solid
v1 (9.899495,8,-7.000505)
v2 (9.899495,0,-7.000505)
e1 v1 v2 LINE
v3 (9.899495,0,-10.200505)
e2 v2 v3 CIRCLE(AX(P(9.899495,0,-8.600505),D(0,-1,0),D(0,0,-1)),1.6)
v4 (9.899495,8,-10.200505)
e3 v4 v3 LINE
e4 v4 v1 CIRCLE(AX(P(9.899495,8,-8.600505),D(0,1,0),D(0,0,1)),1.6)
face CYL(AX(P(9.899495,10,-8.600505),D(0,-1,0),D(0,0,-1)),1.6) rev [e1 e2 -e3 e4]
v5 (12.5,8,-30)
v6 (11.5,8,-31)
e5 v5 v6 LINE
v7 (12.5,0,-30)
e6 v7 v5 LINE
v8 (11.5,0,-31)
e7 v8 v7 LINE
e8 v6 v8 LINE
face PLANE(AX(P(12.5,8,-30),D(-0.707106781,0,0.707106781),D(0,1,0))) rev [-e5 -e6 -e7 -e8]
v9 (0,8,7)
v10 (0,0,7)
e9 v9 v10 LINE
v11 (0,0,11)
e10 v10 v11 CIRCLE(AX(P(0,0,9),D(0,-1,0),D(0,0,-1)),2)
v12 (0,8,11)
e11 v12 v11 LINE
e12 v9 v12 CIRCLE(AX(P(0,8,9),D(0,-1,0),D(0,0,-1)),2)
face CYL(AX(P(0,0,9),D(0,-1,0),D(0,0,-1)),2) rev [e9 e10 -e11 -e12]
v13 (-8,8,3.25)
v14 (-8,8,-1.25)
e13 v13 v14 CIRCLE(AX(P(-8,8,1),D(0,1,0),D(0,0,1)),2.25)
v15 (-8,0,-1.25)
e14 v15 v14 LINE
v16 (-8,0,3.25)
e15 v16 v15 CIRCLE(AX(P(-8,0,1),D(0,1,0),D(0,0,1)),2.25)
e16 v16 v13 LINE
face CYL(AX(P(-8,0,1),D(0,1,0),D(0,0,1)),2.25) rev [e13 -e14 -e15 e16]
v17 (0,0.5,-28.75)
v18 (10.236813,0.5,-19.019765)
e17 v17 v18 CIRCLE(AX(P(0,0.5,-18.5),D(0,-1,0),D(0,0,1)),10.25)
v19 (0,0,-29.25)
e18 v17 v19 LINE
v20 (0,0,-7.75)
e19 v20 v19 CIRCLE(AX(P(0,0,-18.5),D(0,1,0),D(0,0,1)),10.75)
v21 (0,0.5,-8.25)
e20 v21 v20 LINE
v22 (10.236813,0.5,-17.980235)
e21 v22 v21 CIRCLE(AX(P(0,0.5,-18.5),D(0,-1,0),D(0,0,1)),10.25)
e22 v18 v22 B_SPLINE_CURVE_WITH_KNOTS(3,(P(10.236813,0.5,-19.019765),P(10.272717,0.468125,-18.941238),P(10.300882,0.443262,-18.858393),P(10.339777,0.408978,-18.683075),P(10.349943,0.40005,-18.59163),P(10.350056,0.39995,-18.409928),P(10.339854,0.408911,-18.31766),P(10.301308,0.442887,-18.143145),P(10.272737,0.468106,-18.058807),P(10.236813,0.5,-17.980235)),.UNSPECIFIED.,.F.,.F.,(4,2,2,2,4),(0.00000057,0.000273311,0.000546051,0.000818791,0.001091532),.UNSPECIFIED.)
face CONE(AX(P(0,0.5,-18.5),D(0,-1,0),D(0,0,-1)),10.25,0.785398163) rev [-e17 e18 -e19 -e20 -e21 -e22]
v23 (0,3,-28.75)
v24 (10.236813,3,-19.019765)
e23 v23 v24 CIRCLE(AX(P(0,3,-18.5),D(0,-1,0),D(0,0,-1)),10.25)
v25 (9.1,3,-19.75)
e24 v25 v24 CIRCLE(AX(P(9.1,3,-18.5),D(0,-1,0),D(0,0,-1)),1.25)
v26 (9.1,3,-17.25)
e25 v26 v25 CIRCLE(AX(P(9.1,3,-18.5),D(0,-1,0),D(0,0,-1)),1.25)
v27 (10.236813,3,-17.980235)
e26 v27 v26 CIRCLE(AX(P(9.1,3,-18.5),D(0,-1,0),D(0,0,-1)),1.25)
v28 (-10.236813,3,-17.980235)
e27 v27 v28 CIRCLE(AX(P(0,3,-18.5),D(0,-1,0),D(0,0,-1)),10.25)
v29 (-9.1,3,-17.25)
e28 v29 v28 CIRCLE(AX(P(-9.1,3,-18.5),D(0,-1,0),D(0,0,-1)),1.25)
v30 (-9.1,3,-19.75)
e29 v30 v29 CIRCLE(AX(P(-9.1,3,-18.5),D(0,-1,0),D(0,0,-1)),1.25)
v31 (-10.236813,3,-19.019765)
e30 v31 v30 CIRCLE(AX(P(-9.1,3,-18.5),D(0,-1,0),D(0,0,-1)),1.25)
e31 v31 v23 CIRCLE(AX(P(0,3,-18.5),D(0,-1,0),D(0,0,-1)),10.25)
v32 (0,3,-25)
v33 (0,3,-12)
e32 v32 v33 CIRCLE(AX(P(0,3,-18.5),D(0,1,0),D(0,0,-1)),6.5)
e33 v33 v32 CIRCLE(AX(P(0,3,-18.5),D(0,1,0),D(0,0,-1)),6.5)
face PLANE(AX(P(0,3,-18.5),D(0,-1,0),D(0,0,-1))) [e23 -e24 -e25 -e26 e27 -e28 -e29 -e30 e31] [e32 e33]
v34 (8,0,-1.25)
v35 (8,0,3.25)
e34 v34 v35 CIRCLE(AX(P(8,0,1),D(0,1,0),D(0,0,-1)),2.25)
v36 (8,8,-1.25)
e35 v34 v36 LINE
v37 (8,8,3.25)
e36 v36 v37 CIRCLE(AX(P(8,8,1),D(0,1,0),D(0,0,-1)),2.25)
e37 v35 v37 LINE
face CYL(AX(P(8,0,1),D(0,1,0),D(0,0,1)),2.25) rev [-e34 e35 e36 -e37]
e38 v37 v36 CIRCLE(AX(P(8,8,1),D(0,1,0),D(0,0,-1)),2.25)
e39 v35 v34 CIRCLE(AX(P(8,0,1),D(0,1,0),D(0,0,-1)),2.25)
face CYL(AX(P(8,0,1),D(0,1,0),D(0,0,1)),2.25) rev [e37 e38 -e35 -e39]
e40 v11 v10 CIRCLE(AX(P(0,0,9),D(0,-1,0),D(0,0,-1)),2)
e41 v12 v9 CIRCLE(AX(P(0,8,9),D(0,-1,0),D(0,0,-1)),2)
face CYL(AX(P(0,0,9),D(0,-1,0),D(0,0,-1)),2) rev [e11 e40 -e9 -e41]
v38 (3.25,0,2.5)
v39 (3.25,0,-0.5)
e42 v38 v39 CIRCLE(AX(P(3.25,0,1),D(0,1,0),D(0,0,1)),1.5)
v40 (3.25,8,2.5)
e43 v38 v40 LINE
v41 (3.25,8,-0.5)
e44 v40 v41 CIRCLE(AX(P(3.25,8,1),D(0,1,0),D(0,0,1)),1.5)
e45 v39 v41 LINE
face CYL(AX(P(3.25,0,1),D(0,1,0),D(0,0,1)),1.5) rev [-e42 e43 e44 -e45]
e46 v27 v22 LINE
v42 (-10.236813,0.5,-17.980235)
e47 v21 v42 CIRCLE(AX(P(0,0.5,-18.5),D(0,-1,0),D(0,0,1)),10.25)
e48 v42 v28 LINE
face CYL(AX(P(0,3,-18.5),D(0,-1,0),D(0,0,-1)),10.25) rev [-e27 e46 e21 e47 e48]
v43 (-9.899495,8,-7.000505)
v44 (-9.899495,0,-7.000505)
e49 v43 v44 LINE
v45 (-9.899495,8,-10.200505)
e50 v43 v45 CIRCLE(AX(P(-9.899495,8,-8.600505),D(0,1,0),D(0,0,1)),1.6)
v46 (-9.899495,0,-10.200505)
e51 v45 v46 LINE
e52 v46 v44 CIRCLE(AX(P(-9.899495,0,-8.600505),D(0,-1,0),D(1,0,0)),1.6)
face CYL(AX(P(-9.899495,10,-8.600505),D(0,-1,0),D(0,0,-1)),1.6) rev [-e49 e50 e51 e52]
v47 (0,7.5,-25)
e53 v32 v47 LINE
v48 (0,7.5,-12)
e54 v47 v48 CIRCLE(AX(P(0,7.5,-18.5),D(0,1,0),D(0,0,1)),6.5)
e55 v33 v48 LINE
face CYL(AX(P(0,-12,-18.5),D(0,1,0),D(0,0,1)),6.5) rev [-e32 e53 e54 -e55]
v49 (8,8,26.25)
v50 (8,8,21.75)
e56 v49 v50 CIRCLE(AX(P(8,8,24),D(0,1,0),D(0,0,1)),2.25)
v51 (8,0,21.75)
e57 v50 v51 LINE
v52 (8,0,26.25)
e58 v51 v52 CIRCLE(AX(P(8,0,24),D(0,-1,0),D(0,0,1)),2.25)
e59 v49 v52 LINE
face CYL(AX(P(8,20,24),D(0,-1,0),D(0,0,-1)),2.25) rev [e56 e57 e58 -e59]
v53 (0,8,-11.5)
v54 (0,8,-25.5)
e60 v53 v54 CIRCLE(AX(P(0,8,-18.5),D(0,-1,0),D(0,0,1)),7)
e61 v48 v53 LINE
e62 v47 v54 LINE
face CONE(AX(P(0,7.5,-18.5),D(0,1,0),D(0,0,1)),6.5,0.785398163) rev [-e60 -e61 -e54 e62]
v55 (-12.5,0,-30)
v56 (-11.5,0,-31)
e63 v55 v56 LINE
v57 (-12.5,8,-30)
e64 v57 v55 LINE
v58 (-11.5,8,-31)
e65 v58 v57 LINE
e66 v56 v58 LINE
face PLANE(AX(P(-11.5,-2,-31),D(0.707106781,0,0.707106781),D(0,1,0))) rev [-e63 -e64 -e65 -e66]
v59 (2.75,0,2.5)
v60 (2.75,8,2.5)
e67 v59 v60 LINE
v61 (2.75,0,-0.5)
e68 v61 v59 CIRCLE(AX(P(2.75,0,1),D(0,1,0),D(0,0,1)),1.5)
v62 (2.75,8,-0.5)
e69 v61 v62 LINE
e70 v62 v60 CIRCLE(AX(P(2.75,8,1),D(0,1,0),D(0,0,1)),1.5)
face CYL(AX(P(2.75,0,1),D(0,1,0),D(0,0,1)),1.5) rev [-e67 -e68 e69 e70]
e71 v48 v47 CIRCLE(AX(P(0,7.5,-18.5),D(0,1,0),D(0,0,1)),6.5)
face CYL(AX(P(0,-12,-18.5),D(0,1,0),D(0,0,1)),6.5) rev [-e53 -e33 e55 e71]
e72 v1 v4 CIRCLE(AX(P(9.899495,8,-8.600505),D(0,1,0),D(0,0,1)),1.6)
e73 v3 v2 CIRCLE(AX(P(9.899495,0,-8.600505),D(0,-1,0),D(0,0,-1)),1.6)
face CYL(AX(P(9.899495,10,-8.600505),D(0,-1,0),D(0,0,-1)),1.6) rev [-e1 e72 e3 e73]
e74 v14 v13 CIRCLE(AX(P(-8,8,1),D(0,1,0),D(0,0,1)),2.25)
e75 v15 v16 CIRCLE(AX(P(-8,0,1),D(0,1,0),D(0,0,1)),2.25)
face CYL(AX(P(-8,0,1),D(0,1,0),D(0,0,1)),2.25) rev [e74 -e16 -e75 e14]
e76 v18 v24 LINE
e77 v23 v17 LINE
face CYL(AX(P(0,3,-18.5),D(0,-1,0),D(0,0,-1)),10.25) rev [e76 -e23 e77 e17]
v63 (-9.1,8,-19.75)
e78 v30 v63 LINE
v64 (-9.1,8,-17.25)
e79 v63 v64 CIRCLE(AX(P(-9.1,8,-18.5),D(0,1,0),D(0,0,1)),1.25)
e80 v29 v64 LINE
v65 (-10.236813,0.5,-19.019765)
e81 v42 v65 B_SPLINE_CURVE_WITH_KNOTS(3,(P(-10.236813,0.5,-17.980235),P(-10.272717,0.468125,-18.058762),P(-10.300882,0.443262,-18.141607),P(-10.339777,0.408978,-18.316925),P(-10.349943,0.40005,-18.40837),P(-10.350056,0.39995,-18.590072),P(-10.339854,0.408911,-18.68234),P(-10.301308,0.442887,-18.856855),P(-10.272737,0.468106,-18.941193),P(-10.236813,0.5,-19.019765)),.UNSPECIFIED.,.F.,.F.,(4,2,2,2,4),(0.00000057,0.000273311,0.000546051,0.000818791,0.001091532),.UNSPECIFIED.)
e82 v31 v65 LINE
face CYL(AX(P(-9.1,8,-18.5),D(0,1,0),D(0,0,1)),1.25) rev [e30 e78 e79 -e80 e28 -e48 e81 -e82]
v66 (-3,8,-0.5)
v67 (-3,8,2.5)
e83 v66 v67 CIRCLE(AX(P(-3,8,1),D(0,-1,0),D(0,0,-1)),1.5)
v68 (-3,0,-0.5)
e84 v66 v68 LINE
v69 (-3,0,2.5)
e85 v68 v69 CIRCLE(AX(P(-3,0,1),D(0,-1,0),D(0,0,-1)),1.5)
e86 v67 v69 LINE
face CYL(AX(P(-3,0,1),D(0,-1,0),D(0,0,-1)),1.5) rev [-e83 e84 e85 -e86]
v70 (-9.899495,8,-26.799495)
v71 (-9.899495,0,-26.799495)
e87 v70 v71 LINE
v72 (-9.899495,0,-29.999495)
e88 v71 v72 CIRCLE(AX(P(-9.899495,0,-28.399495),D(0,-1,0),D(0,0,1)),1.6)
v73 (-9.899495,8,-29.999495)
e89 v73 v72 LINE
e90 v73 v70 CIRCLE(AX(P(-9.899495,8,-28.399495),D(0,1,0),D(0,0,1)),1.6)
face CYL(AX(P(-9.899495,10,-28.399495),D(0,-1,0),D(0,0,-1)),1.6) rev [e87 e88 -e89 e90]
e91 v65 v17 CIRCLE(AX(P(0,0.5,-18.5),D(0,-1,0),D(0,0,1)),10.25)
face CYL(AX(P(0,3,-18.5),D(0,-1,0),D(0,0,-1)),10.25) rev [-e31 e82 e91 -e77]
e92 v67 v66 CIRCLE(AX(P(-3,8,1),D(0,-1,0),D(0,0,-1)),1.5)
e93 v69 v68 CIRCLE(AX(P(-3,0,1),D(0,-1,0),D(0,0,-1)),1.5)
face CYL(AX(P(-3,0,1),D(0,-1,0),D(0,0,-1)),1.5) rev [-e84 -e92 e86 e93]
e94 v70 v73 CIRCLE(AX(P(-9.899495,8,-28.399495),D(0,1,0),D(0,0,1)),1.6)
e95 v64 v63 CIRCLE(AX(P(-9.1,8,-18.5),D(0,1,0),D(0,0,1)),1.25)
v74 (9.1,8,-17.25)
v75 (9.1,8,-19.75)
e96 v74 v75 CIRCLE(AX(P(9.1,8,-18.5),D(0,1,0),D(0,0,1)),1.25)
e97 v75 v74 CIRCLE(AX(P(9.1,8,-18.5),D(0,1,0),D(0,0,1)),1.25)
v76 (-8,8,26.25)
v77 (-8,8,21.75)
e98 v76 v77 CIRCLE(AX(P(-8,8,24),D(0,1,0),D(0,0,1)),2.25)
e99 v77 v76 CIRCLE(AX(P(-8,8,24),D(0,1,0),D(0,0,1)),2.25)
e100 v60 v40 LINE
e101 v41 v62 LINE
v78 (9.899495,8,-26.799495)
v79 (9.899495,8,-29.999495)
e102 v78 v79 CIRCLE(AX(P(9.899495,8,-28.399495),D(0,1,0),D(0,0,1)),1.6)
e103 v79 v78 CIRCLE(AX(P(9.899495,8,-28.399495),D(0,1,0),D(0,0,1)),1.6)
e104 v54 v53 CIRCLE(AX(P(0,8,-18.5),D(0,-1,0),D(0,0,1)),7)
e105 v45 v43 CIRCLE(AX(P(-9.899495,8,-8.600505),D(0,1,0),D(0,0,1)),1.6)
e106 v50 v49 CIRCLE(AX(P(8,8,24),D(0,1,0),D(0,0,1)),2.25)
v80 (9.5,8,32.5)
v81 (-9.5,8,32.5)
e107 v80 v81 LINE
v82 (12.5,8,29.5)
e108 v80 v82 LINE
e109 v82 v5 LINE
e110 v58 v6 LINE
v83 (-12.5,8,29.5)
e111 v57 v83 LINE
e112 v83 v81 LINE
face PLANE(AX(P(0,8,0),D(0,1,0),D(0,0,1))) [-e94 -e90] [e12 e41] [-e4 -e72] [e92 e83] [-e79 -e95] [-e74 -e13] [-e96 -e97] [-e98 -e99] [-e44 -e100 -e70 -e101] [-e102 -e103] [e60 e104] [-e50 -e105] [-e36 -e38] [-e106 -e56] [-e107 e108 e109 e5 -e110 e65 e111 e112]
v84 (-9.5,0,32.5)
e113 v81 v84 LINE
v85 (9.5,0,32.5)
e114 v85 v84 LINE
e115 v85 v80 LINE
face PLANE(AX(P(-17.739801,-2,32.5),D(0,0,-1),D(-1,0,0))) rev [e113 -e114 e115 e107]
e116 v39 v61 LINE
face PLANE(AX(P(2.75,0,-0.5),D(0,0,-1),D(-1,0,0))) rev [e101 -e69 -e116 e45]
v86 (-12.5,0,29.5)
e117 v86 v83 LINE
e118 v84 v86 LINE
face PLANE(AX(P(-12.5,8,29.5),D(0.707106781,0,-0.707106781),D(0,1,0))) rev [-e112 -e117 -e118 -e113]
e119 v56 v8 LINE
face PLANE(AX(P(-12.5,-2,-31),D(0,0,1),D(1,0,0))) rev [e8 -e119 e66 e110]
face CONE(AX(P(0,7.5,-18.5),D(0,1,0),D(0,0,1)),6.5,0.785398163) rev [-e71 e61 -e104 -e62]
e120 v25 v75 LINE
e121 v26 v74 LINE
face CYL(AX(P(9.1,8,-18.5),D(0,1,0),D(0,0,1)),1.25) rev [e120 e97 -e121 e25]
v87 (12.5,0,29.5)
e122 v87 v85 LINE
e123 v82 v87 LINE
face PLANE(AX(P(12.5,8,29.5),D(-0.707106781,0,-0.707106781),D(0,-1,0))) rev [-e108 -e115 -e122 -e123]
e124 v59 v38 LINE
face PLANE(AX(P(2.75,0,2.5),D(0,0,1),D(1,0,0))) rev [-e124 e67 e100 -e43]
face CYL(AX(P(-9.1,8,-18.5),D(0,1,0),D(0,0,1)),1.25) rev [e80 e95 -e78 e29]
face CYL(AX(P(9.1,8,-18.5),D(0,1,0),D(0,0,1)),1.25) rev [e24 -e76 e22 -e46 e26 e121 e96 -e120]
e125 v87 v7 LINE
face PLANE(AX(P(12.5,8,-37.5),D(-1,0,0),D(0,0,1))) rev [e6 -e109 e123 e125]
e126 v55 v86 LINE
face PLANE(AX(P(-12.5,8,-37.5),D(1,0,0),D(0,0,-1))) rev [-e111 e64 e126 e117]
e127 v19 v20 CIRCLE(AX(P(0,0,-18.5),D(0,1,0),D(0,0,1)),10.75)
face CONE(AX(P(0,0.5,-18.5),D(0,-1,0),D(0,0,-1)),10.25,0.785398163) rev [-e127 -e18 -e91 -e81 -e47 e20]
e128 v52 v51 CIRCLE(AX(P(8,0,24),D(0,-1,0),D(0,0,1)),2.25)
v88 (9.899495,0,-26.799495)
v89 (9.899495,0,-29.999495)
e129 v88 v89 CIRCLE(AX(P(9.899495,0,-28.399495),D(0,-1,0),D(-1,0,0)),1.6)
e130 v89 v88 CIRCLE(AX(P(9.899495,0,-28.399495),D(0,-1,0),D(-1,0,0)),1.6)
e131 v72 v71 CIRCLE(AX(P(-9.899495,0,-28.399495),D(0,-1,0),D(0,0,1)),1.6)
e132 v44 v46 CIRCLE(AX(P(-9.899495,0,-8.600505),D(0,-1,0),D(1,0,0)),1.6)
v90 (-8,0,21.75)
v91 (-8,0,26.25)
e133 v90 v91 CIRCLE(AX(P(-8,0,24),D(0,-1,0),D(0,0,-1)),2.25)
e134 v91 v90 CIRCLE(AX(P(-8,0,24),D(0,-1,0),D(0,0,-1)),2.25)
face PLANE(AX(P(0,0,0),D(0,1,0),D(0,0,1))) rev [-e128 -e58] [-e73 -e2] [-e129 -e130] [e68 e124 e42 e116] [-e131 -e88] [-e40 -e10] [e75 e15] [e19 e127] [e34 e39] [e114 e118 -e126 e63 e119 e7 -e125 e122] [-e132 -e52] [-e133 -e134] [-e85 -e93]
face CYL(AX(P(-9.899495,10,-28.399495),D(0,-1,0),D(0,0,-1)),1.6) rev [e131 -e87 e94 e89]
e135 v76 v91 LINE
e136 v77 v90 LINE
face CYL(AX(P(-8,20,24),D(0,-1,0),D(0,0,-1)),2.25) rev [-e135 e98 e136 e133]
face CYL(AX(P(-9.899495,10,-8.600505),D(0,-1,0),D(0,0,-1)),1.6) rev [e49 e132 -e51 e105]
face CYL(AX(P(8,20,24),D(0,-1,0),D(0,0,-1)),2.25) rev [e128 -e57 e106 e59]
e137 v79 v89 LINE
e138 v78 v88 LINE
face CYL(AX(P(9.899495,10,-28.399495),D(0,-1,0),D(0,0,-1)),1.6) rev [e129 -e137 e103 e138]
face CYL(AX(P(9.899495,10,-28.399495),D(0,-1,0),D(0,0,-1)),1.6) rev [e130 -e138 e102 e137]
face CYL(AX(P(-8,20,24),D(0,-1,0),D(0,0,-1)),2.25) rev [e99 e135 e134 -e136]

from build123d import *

# Parameters (mm, degrees)
SKETCH1_W                = 25
SKETCH1_H                = 75
BOSS_EXTRUDE1_DEPTH      = 8
SKETCH2_R                = 2.25
CUT_EXTRUDE1_DEPTH       = 20
SKETCH3_R                = 6.5
CUT_EXTRUDE2_DEPTH       = 20
SKETCH4_W                = 35.479601552
SKETCH4_H                = 10
CUT_EXTRUDE3_DEPTH       = 10
SKETCH5_W                = 25
SKETCH5_H                = 6.5
CUT_EXTRUDE4_DEPTH       = 10
CHAMFER1_SIZE            = 3
SKETCH6_R                = 1.6
CUT_EXTRUDE5_DEPTH       = 10
CIRPATTERN1_COUNT        = 4
SKETCH7_R                = 10.25
CUT_EXTRUDE6_DEPTH       = 3
SKETCH8_R                = 2.25
CUT_EXTRUDE7_DEPTH       = 36.72814017
CHAMFER2_SIZE            = 1
F_3_0_3_DIAMETER_HOLE1_D = 3
F_4_0_4_DIAMETER_HOLE1_D = 4
CUT_EXTRUDE8_DEPTH       = 36.72814017
CHAMFER3_SIZE            = 0.5
M3_TAPPED_HOLE1_D        = 2.5
M3_TAPPED_HOLE1_DEPTH    = 8.5
M3_TAPPED_HOLE1_TIP      = 0.751075774


with BuildPart() as part:
    # Sketch1 → Boss-Extrude1 (new body)
    with BuildSketch(Plane(origin=(0, 0, 0), x_dir=(1, 0, 0), z_dir=(0, 1, 0))):
        Rectangle(SKETCH1_W, SKETCH1_H)
    extrude(amount=BOSS_EXTRUDE1_DEPTH)

    # Sketch2 → Cut-Extrude1 (cut)
    with BuildSketch(Plane.XZ):
        with Locations(Location((-8, 24, 0), (0, 0, 270))):
            Circle(SKETCH2_R)
        with Locations(Location((8, 24, 0), (0, 0, 90))):
            Circle(SKETCH2_R)
    extrude(amount=-CUT_EXTRUDE1_DEPTH, mode=Mode.SUBTRACT)

    # Sketch3 → Cut-Extrude2 (cut)
    with BuildSketch(Plane(origin=(0, 8, 0), x_dir=(1, 0, 0), z_dir=(0, 1, 0))):
        with Locations(Location((0, 18.5, 0), (0, 0, 270))):
            Circle(SKETCH3_R)
    extrude(amount=-CUT_EXTRUDE2_DEPTH, mode=Mode.SUBTRACT)

    # Sketch4 → Cut-Extrude3 (cut)
    with BuildSketch(Plane(origin=(0, 8, 0), x_dir=(1, 0, 0), z_dir=(0, 1, 0))):
        with Locations((0, -37.5)):
            Rectangle(SKETCH4_W, SKETCH4_H)
    extrude(amount=-CUT_EXTRUDE3_DEPTH, mode=Mode.SUBTRACT)

    # Sketch5 → Cut-Extrude4 (cut)
    with BuildSketch(Plane(origin=(0, 8, 0), x_dir=(1, 0, 0), z_dir=(0, 1, 0))):
        with Locations((0, 34.25)):
            Rectangle(SKETCH5_W, SKETCH5_H)
    extrude(amount=-CUT_EXTRUDE4_DEPTH, mode=Mode.SUBTRACT)

    # Chamfer1
    chamfer1_edges = [part.edges().sort_by_distance(p)[0] for p in [
        (12.5, 4, 32.5),
        (-12.5, 4, 32.5),
    ]]
    chamfer(chamfer1_edges, length=CHAMFER1_SIZE)

    # Sketch6 → Cut-Extrude5 (cut)
    with BuildSketch(Plane.XZ):
        with Locations(Location((9.899494937, -8.600505063, 0), (0, 0, 270))):
            Circle(SKETCH6_R)
    cut_extrude5 = extrude(amount=-CUT_EXTRUDE5_DEPTH, mode=Mode.SUBTRACT)

    # CirPattern1: Cut-Extrude5 ×4 about axis
    cirpattern1_axis = Axis((0, 0, -18.5), (0, 1, 0))
    for i in range(1, CIRPATTERN1_COUNT):
        add(cut_extrude5.rotate(cirpattern1_axis, i * 360 / CIRPATTERN1_COUNT), mode=Mode.SUBTRACT)

    # Sketch7 → Cut-Extrude6 (cut)
    with BuildSketch(Plane.XZ):
        with Locations(Location((0, -18.5, 0), (0, 0, 270))):
            Circle(SKETCH7_R)
    extrude(amount=-CUT_EXTRUDE6_DEPTH, mode=Mode.SUBTRACT)

    # Sketch8 → Cut-Extrude7 (cut, through all)
    with BuildSketch(Plane(origin=(0, 8, 0), x_dir=(1, 0, 0), z_dir=(0, 1, 0))):
        with Locations(Location((-8, -1, 0), (0, 0, 270))):
            Circle(SKETCH8_R)
        with Locations(Location((8, -1, 0), (0, 0, 90))):
            Circle(SKETCH8_R)
    extrude(amount=-CUT_EXTRUDE7_DEPTH, mode=Mode.SUBTRACT)

    # Chamfer2
    chamfer2_edges = [part.edges().sort_by_distance(p)[0] for p in [
        (-12.5, 4, -31),
        (12.5, 4, -31),
    ]]
    chamfer(chamfer2_edges, length=CHAMFER2_SIZE)

    # Ø3.0 (3) Diameter Hole1 (through all)
    with Locations(Plane(origin=(0, 0, 0), x_dir=(-1, 0, 0), z_dir=(0, -1, 0))):
        with Locations((3, -1), (-3, -1)):
            Hole(F_3_0_3_DIAMETER_HOLE1_D / 2)

    # Ø4.0 (4) Diameter Hole1 (through all)
    with Locations(Plane(origin=(0, 0, 0), x_dir=(-1, 0, 0), z_dir=(0, -1, 0))):
        with Locations((0, -9)):
            Hole(F_4_0_4_DIAMETER_HOLE1_D / 2)

    # Sketch14 → Cut-Extrude8 (cut, through all)
    with BuildSketch(Plane(origin=(0, 8, 0), x_dir=(1, 0, 0), z_dir=(0, 1, 0))):
        with BuildLine():
            Line((2.75, 0.5), (3.25, 0.5))
            ThreePointArc((3.25, 0.5), (4.75, -1), (3.25, -2.5))
            Line((3.25, -2.5), (2.75, -2.5))
            ThreePointArc((2.75, -2.5), (1.25, -1), (2.75, 0.5))
        make_face()
    extrude(amount=-CUT_EXTRUDE8_DEPTH, mode=Mode.SUBTRACT)

    # Chamfer3
    chamfer3_edges = [part.edges().sort_by_distance(p)[0] for p in [
        (0, 0, -8.25),
        (0, 8, -25),
    ]]
    chamfer(chamfer3_edges, length=CHAMFER3_SIZE)

    # M3 Tapped Hole1
    with Locations(Plane(origin=(0, 8, 0), x_dir=(1, 0, 0), z_dir=(0, 1, 0))):
        with Locations((-9.1, 18.5), (9.1, 18.5)):
            Hole(M3_TAPPED_HOLE1_D / 2, depth=M3_TAPPED_HOLE1_DEPTH)
            with Locations((0, 0, -(M3_TAPPED_HOLE1_DEPTH + M3_TAPPED_HOLE1_TIP / 2))):  # 118° drill point
                Cone(0, M3_TAPPED_HOLE1_D / 2, M3_TAPPED_HOLE1_TIP, mode=Mode.SUBTRACT)


solid = part.part
